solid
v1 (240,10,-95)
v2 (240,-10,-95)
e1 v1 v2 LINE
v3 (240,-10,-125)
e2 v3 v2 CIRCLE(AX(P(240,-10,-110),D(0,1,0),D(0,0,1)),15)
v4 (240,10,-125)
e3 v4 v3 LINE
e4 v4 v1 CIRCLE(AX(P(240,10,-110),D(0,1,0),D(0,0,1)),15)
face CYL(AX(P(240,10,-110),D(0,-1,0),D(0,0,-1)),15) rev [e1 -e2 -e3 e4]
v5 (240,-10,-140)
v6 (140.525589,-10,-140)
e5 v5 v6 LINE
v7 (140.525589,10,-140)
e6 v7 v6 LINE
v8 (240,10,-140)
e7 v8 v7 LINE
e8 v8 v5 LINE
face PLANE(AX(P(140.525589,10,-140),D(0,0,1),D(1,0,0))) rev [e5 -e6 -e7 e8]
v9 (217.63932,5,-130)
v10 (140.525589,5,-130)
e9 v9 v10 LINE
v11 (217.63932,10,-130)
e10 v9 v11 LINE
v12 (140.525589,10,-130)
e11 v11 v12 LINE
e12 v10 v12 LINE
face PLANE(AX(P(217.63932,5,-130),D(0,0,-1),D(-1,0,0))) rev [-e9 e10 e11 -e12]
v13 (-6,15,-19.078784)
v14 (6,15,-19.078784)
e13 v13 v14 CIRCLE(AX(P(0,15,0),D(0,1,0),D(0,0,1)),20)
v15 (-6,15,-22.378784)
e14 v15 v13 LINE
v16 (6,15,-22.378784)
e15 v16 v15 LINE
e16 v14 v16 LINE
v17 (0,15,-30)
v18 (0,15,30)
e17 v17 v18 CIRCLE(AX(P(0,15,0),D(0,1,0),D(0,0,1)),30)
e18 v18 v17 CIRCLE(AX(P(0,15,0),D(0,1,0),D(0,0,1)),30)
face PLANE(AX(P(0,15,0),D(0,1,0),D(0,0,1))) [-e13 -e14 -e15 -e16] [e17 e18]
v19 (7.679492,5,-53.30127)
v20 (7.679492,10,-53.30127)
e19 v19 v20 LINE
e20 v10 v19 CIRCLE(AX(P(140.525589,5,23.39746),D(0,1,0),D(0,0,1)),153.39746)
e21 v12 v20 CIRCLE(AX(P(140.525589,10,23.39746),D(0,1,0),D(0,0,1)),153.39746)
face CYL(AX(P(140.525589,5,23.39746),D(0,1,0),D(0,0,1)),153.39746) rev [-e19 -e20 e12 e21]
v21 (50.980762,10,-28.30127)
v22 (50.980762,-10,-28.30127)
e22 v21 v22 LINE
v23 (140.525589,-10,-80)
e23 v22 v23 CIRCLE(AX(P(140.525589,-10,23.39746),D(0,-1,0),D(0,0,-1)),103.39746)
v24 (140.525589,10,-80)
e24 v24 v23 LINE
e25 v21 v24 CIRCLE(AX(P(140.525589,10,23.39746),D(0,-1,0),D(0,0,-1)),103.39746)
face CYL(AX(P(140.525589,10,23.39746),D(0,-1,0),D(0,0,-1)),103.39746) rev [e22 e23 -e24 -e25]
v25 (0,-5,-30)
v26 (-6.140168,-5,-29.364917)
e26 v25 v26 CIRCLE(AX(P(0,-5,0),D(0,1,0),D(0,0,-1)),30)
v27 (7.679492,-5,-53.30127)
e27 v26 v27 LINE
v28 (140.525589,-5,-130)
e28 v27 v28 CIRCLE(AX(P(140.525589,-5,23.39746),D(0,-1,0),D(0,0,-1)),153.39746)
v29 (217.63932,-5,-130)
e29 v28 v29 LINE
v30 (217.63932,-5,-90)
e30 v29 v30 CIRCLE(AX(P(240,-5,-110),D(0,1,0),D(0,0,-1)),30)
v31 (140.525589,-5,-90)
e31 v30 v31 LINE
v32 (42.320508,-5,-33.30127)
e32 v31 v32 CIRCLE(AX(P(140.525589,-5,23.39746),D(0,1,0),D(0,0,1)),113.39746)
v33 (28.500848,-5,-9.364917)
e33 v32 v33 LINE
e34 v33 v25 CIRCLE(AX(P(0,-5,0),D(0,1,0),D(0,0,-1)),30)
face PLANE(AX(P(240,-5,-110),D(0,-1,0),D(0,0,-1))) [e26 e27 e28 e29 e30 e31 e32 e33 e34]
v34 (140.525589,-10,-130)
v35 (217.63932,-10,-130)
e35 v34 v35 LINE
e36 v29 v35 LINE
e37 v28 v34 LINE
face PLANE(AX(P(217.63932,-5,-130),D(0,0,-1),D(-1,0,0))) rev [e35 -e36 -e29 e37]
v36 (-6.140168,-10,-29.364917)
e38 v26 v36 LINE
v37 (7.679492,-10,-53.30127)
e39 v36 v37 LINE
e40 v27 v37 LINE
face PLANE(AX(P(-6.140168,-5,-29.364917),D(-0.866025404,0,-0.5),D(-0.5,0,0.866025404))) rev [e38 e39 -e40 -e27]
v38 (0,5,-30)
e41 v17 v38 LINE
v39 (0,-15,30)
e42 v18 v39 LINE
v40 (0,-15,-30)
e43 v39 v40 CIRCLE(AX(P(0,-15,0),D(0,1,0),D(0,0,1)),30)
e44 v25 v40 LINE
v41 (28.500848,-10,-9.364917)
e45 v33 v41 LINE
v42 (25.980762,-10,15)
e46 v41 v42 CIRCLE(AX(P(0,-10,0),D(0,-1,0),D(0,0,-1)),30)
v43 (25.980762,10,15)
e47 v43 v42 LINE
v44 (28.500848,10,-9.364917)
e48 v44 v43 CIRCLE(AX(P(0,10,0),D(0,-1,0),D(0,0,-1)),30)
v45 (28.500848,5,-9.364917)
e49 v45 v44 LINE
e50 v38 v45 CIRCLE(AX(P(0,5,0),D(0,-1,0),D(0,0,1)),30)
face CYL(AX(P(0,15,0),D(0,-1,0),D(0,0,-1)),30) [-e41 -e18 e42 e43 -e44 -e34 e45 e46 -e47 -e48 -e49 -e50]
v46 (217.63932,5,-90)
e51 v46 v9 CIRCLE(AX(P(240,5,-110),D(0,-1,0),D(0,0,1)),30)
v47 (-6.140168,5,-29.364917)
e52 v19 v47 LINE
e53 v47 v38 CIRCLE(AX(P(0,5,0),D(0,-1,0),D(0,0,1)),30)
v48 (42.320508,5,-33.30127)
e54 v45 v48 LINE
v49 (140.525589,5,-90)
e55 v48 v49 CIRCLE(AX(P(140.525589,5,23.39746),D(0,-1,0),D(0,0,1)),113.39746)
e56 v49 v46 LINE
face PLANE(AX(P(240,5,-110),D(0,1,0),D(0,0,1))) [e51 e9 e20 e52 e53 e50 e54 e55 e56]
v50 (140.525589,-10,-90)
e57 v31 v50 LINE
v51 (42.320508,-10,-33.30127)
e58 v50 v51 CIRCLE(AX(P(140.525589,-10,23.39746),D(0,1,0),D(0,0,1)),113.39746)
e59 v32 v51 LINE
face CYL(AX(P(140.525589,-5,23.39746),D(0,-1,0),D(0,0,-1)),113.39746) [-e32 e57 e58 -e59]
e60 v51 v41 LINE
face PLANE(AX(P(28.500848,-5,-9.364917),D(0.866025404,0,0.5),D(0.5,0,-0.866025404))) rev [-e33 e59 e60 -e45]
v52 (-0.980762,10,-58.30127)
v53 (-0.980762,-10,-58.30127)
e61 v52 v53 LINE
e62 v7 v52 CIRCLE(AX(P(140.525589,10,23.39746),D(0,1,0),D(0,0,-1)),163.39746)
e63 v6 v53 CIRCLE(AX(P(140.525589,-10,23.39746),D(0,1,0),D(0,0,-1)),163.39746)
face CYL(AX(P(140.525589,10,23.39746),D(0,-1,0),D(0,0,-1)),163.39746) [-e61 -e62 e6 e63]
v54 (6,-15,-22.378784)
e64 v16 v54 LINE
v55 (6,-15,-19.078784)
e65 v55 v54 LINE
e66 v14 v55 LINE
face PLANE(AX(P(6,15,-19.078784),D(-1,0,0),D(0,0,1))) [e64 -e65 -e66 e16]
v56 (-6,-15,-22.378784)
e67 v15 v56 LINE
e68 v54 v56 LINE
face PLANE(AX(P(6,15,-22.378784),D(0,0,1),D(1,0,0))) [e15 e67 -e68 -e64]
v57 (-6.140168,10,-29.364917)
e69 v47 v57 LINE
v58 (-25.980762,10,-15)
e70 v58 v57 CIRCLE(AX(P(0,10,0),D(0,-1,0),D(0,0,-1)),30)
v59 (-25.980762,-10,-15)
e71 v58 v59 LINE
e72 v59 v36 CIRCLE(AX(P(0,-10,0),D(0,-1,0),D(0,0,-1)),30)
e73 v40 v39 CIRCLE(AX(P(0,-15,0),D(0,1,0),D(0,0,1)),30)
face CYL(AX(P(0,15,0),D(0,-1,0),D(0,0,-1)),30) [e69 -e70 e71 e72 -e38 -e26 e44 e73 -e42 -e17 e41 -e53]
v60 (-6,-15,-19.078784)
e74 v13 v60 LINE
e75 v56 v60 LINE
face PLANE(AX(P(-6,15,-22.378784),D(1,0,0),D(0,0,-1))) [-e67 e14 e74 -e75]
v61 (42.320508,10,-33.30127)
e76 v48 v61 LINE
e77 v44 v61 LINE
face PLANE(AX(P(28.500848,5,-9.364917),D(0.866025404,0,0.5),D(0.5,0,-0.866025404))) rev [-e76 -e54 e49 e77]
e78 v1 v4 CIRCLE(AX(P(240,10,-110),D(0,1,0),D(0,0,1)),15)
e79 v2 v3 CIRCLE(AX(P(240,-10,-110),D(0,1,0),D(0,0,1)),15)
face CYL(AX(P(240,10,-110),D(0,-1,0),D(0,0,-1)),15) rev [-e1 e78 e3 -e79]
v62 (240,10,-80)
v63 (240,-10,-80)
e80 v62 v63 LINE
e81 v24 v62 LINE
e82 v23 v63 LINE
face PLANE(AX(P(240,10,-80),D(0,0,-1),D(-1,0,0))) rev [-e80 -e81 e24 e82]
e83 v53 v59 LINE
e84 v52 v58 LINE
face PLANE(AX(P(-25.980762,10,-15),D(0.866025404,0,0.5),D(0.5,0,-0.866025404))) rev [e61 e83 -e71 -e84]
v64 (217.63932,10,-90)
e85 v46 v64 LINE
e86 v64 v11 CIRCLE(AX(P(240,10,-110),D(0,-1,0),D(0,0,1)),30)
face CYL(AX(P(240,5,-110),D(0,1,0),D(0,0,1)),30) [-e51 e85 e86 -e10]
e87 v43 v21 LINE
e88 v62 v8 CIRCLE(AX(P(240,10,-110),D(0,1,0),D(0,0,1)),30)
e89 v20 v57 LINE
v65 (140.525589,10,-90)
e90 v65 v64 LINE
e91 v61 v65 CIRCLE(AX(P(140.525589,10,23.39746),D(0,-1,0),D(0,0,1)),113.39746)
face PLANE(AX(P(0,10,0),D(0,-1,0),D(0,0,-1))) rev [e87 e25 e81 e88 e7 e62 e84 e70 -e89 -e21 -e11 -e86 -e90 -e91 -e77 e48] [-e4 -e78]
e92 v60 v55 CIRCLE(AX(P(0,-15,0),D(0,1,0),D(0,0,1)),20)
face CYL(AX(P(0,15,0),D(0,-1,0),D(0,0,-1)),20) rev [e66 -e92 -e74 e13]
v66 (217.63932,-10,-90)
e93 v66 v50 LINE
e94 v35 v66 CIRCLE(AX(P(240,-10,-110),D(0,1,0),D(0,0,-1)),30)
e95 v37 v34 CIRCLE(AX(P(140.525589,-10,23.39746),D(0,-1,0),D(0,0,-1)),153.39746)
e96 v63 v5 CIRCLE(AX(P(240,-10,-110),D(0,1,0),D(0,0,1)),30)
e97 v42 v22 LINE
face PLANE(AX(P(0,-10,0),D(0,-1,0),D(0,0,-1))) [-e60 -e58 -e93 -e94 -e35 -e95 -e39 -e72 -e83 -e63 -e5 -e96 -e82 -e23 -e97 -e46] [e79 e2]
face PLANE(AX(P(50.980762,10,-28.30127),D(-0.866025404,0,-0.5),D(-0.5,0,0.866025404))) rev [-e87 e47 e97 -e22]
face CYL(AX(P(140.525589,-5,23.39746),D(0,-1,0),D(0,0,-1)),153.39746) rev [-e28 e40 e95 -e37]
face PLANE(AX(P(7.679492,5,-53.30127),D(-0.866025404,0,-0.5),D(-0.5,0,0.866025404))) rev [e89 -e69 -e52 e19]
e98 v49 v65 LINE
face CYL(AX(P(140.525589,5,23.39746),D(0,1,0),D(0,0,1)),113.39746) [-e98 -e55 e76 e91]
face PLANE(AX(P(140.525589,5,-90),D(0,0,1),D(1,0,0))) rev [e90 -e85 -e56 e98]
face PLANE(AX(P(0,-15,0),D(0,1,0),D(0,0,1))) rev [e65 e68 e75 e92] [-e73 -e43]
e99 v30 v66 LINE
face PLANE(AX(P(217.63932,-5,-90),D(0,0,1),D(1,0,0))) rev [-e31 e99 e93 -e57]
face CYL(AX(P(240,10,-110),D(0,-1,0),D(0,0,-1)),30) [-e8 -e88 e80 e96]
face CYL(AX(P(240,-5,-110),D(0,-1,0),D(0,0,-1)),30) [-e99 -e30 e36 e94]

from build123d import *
from build123d.topology import SkipClean

# Parameters (mm, degrees)
SKETCH_1_R          = 30
EXTRUDE_1_DEPTH     = 15
SKETCH_2_R          = 15
EXTRUDE_2_DEPTH     = 10
SKETCH_3_R          = 30
SKETCH_3_R_2        = 15
EXTRUDE_3_DEPTH     = 10
CUT_EXTRUDE_1_DEPTH = 5
CUT_EXTRUDE_START   = -5
CUT_EXTRUDE_2_DEPTH = 5


with BuildPart() as part:
    # 草图1 → 凸台-拉伸1 (new, symmetric)
    with BuildSketch(Plane(origin=(0, 0, 0), x_dir=(1, 0, 0), z_dir=(0, 1, 0))):
        with Locations(Location((0, 0, 0), (0, 0, 270))):
            Circle(SKETCH_1_R)
        with BuildLine():
            Line((6, 19.078784028), (6, 22.378784028))
            Line((6, 22.378784028), (-6, 22.378784028))
            Line((-6, 22.378784028), (-6, 19.078784028))
            ThreePointArc((-6, 19.078784028), (0, -20), (6, 19.078784028))
        make_face(mode=Mode.SUBTRACT)
    extrude(amount=EXTRUDE_1_DEPTH, both=True)

    # 草图2 → 凸台-拉伸2 (add, symmetric)
    with BuildSketch(Plane(origin=(0, 0, 0), x_dir=(1, 0, 0), z_dir=(0, 1, 0))):
        with BuildLine():
            Line((-25.980762114, 15), (-0.980762114, 58.301270189))
            ThreePointArc((-0.980762114, 58.301270189), (58.826859022, 118.108891325), (140.525588833, 140))
            Line((140.525588833, 140), (240, 140))
            ThreePointArc((240, 140), (270, 110), (240, 80))
            Line((240, 80), (140.525588833, 80))
            ThreePointArc((140.525588833, 80), (88.826859022, 66.147367097), (50.980762114, 28.301270189))
            Line((50.980762114, 28.301270189), (25.980762114, -15))
            ThreePointArc((25.980762114, -15), (15, 25.980762114), (-25.980762114, 15))
        make_face()
        with Locations(Location((240, 110, 0), (0, 0, 270))):
            Circle(SKETCH_2_R, mode=Mode.SUBTRACT)
    extrude(amount=EXTRUDE_2_DEPTH, both=True)

    # 草图3 → 凸台-拉伸3 (add, symmetric)
    with BuildSketch(Plane(origin=(0, 0, 0), x_dir=(1, 0, 0), z_dir=(0, 1, 0))):
        with Locations((240, 110)):
            Circle(SKETCH_3_R)
        with Locations(Location((240, 110, 0), (0, 0, 270))):
            Circle(SKETCH_3_R_2, mode=Mode.SUBTRACT)
    extrude(amount=EXTRUDE_3_DEPTH, both=True)

    # 草图4 → 切除-拉伸1 (cut)
    with SkipClean():  # the faces are left unmerged after this step: merging them gives an invalid solid
        with BuildSketch(Plane(origin=(0, 10, 0), x_dir=(1, 0, 0), z_dir=(0, 1, 0))):
            with BuildLine():
                Line((217.639320225, 130), (140.525588833, 130))
                ThreePointArc((140.525588833, 130), (63.826859022, 109.448637287), (7.679491924, 53.301270189))
                Line((7.679491924, 53.301270189), (-6.140168188, 29.364916731))
                ThreePointArc((-6.140168188, 29.364916731), (15, 25.980762114), (28.500847963, 9.364916731))
                Line((28.500847963, 9.364916731), (42.320508076, 33.301270189))
                ThreePointArc((42.320508076, 33.301270189), (83.826859022, 74.807621135), (140.525588833, 90))
                Line((140.525588833, 90), (217.639320225, 90))
                ThreePointArc((217.639320225, 90), (210, 110), (217.639320225, 130))
            make_face()
        extrude(amount=-CUT_EXTRUDE_1_DEPTH, mode=Mode.SUBTRACT)

    # 草图5 → 切除-拉伸2 (cut)
    with SkipClean():  # the faces are left unmerged after this step: merging them gives an invalid solid
        with BuildSketch(Plane.XZ.offset(10).offset(CUT_EXTRUDE_START)):
            with BuildLine():
                Line((217.639320225, -90), (140.525588833, -90))
                ThreePointArc((140.525588833, -90), (83.826859022, -74.807621135), (42.320508076, -33.301270189))
                Line((42.320508076, -33.301270189), (28.500847963, -9.364916731))
                ThreePointArc((28.500847963, -9.364916731), (15, -25.980762114), (-6.140168188, -29.364916731))
                Line((-6.140168188, -29.364916731), (7.679491924, -53.301270189))
                ThreePointArc((7.679491924, -53.301270189), (63.826859022, -109.448637287), (140.525588833, -130))
                Line((140.525588833, -130), (217.639320225, -130))
                ThreePointArc((217.639320225, -130), (210, -110), (217.639320225, -90))
            make_face()
        extrude(amount=CUT_EXTRUDE_2_DEPTH, mode=Mode.SUBTRACT)


solid = part.part
